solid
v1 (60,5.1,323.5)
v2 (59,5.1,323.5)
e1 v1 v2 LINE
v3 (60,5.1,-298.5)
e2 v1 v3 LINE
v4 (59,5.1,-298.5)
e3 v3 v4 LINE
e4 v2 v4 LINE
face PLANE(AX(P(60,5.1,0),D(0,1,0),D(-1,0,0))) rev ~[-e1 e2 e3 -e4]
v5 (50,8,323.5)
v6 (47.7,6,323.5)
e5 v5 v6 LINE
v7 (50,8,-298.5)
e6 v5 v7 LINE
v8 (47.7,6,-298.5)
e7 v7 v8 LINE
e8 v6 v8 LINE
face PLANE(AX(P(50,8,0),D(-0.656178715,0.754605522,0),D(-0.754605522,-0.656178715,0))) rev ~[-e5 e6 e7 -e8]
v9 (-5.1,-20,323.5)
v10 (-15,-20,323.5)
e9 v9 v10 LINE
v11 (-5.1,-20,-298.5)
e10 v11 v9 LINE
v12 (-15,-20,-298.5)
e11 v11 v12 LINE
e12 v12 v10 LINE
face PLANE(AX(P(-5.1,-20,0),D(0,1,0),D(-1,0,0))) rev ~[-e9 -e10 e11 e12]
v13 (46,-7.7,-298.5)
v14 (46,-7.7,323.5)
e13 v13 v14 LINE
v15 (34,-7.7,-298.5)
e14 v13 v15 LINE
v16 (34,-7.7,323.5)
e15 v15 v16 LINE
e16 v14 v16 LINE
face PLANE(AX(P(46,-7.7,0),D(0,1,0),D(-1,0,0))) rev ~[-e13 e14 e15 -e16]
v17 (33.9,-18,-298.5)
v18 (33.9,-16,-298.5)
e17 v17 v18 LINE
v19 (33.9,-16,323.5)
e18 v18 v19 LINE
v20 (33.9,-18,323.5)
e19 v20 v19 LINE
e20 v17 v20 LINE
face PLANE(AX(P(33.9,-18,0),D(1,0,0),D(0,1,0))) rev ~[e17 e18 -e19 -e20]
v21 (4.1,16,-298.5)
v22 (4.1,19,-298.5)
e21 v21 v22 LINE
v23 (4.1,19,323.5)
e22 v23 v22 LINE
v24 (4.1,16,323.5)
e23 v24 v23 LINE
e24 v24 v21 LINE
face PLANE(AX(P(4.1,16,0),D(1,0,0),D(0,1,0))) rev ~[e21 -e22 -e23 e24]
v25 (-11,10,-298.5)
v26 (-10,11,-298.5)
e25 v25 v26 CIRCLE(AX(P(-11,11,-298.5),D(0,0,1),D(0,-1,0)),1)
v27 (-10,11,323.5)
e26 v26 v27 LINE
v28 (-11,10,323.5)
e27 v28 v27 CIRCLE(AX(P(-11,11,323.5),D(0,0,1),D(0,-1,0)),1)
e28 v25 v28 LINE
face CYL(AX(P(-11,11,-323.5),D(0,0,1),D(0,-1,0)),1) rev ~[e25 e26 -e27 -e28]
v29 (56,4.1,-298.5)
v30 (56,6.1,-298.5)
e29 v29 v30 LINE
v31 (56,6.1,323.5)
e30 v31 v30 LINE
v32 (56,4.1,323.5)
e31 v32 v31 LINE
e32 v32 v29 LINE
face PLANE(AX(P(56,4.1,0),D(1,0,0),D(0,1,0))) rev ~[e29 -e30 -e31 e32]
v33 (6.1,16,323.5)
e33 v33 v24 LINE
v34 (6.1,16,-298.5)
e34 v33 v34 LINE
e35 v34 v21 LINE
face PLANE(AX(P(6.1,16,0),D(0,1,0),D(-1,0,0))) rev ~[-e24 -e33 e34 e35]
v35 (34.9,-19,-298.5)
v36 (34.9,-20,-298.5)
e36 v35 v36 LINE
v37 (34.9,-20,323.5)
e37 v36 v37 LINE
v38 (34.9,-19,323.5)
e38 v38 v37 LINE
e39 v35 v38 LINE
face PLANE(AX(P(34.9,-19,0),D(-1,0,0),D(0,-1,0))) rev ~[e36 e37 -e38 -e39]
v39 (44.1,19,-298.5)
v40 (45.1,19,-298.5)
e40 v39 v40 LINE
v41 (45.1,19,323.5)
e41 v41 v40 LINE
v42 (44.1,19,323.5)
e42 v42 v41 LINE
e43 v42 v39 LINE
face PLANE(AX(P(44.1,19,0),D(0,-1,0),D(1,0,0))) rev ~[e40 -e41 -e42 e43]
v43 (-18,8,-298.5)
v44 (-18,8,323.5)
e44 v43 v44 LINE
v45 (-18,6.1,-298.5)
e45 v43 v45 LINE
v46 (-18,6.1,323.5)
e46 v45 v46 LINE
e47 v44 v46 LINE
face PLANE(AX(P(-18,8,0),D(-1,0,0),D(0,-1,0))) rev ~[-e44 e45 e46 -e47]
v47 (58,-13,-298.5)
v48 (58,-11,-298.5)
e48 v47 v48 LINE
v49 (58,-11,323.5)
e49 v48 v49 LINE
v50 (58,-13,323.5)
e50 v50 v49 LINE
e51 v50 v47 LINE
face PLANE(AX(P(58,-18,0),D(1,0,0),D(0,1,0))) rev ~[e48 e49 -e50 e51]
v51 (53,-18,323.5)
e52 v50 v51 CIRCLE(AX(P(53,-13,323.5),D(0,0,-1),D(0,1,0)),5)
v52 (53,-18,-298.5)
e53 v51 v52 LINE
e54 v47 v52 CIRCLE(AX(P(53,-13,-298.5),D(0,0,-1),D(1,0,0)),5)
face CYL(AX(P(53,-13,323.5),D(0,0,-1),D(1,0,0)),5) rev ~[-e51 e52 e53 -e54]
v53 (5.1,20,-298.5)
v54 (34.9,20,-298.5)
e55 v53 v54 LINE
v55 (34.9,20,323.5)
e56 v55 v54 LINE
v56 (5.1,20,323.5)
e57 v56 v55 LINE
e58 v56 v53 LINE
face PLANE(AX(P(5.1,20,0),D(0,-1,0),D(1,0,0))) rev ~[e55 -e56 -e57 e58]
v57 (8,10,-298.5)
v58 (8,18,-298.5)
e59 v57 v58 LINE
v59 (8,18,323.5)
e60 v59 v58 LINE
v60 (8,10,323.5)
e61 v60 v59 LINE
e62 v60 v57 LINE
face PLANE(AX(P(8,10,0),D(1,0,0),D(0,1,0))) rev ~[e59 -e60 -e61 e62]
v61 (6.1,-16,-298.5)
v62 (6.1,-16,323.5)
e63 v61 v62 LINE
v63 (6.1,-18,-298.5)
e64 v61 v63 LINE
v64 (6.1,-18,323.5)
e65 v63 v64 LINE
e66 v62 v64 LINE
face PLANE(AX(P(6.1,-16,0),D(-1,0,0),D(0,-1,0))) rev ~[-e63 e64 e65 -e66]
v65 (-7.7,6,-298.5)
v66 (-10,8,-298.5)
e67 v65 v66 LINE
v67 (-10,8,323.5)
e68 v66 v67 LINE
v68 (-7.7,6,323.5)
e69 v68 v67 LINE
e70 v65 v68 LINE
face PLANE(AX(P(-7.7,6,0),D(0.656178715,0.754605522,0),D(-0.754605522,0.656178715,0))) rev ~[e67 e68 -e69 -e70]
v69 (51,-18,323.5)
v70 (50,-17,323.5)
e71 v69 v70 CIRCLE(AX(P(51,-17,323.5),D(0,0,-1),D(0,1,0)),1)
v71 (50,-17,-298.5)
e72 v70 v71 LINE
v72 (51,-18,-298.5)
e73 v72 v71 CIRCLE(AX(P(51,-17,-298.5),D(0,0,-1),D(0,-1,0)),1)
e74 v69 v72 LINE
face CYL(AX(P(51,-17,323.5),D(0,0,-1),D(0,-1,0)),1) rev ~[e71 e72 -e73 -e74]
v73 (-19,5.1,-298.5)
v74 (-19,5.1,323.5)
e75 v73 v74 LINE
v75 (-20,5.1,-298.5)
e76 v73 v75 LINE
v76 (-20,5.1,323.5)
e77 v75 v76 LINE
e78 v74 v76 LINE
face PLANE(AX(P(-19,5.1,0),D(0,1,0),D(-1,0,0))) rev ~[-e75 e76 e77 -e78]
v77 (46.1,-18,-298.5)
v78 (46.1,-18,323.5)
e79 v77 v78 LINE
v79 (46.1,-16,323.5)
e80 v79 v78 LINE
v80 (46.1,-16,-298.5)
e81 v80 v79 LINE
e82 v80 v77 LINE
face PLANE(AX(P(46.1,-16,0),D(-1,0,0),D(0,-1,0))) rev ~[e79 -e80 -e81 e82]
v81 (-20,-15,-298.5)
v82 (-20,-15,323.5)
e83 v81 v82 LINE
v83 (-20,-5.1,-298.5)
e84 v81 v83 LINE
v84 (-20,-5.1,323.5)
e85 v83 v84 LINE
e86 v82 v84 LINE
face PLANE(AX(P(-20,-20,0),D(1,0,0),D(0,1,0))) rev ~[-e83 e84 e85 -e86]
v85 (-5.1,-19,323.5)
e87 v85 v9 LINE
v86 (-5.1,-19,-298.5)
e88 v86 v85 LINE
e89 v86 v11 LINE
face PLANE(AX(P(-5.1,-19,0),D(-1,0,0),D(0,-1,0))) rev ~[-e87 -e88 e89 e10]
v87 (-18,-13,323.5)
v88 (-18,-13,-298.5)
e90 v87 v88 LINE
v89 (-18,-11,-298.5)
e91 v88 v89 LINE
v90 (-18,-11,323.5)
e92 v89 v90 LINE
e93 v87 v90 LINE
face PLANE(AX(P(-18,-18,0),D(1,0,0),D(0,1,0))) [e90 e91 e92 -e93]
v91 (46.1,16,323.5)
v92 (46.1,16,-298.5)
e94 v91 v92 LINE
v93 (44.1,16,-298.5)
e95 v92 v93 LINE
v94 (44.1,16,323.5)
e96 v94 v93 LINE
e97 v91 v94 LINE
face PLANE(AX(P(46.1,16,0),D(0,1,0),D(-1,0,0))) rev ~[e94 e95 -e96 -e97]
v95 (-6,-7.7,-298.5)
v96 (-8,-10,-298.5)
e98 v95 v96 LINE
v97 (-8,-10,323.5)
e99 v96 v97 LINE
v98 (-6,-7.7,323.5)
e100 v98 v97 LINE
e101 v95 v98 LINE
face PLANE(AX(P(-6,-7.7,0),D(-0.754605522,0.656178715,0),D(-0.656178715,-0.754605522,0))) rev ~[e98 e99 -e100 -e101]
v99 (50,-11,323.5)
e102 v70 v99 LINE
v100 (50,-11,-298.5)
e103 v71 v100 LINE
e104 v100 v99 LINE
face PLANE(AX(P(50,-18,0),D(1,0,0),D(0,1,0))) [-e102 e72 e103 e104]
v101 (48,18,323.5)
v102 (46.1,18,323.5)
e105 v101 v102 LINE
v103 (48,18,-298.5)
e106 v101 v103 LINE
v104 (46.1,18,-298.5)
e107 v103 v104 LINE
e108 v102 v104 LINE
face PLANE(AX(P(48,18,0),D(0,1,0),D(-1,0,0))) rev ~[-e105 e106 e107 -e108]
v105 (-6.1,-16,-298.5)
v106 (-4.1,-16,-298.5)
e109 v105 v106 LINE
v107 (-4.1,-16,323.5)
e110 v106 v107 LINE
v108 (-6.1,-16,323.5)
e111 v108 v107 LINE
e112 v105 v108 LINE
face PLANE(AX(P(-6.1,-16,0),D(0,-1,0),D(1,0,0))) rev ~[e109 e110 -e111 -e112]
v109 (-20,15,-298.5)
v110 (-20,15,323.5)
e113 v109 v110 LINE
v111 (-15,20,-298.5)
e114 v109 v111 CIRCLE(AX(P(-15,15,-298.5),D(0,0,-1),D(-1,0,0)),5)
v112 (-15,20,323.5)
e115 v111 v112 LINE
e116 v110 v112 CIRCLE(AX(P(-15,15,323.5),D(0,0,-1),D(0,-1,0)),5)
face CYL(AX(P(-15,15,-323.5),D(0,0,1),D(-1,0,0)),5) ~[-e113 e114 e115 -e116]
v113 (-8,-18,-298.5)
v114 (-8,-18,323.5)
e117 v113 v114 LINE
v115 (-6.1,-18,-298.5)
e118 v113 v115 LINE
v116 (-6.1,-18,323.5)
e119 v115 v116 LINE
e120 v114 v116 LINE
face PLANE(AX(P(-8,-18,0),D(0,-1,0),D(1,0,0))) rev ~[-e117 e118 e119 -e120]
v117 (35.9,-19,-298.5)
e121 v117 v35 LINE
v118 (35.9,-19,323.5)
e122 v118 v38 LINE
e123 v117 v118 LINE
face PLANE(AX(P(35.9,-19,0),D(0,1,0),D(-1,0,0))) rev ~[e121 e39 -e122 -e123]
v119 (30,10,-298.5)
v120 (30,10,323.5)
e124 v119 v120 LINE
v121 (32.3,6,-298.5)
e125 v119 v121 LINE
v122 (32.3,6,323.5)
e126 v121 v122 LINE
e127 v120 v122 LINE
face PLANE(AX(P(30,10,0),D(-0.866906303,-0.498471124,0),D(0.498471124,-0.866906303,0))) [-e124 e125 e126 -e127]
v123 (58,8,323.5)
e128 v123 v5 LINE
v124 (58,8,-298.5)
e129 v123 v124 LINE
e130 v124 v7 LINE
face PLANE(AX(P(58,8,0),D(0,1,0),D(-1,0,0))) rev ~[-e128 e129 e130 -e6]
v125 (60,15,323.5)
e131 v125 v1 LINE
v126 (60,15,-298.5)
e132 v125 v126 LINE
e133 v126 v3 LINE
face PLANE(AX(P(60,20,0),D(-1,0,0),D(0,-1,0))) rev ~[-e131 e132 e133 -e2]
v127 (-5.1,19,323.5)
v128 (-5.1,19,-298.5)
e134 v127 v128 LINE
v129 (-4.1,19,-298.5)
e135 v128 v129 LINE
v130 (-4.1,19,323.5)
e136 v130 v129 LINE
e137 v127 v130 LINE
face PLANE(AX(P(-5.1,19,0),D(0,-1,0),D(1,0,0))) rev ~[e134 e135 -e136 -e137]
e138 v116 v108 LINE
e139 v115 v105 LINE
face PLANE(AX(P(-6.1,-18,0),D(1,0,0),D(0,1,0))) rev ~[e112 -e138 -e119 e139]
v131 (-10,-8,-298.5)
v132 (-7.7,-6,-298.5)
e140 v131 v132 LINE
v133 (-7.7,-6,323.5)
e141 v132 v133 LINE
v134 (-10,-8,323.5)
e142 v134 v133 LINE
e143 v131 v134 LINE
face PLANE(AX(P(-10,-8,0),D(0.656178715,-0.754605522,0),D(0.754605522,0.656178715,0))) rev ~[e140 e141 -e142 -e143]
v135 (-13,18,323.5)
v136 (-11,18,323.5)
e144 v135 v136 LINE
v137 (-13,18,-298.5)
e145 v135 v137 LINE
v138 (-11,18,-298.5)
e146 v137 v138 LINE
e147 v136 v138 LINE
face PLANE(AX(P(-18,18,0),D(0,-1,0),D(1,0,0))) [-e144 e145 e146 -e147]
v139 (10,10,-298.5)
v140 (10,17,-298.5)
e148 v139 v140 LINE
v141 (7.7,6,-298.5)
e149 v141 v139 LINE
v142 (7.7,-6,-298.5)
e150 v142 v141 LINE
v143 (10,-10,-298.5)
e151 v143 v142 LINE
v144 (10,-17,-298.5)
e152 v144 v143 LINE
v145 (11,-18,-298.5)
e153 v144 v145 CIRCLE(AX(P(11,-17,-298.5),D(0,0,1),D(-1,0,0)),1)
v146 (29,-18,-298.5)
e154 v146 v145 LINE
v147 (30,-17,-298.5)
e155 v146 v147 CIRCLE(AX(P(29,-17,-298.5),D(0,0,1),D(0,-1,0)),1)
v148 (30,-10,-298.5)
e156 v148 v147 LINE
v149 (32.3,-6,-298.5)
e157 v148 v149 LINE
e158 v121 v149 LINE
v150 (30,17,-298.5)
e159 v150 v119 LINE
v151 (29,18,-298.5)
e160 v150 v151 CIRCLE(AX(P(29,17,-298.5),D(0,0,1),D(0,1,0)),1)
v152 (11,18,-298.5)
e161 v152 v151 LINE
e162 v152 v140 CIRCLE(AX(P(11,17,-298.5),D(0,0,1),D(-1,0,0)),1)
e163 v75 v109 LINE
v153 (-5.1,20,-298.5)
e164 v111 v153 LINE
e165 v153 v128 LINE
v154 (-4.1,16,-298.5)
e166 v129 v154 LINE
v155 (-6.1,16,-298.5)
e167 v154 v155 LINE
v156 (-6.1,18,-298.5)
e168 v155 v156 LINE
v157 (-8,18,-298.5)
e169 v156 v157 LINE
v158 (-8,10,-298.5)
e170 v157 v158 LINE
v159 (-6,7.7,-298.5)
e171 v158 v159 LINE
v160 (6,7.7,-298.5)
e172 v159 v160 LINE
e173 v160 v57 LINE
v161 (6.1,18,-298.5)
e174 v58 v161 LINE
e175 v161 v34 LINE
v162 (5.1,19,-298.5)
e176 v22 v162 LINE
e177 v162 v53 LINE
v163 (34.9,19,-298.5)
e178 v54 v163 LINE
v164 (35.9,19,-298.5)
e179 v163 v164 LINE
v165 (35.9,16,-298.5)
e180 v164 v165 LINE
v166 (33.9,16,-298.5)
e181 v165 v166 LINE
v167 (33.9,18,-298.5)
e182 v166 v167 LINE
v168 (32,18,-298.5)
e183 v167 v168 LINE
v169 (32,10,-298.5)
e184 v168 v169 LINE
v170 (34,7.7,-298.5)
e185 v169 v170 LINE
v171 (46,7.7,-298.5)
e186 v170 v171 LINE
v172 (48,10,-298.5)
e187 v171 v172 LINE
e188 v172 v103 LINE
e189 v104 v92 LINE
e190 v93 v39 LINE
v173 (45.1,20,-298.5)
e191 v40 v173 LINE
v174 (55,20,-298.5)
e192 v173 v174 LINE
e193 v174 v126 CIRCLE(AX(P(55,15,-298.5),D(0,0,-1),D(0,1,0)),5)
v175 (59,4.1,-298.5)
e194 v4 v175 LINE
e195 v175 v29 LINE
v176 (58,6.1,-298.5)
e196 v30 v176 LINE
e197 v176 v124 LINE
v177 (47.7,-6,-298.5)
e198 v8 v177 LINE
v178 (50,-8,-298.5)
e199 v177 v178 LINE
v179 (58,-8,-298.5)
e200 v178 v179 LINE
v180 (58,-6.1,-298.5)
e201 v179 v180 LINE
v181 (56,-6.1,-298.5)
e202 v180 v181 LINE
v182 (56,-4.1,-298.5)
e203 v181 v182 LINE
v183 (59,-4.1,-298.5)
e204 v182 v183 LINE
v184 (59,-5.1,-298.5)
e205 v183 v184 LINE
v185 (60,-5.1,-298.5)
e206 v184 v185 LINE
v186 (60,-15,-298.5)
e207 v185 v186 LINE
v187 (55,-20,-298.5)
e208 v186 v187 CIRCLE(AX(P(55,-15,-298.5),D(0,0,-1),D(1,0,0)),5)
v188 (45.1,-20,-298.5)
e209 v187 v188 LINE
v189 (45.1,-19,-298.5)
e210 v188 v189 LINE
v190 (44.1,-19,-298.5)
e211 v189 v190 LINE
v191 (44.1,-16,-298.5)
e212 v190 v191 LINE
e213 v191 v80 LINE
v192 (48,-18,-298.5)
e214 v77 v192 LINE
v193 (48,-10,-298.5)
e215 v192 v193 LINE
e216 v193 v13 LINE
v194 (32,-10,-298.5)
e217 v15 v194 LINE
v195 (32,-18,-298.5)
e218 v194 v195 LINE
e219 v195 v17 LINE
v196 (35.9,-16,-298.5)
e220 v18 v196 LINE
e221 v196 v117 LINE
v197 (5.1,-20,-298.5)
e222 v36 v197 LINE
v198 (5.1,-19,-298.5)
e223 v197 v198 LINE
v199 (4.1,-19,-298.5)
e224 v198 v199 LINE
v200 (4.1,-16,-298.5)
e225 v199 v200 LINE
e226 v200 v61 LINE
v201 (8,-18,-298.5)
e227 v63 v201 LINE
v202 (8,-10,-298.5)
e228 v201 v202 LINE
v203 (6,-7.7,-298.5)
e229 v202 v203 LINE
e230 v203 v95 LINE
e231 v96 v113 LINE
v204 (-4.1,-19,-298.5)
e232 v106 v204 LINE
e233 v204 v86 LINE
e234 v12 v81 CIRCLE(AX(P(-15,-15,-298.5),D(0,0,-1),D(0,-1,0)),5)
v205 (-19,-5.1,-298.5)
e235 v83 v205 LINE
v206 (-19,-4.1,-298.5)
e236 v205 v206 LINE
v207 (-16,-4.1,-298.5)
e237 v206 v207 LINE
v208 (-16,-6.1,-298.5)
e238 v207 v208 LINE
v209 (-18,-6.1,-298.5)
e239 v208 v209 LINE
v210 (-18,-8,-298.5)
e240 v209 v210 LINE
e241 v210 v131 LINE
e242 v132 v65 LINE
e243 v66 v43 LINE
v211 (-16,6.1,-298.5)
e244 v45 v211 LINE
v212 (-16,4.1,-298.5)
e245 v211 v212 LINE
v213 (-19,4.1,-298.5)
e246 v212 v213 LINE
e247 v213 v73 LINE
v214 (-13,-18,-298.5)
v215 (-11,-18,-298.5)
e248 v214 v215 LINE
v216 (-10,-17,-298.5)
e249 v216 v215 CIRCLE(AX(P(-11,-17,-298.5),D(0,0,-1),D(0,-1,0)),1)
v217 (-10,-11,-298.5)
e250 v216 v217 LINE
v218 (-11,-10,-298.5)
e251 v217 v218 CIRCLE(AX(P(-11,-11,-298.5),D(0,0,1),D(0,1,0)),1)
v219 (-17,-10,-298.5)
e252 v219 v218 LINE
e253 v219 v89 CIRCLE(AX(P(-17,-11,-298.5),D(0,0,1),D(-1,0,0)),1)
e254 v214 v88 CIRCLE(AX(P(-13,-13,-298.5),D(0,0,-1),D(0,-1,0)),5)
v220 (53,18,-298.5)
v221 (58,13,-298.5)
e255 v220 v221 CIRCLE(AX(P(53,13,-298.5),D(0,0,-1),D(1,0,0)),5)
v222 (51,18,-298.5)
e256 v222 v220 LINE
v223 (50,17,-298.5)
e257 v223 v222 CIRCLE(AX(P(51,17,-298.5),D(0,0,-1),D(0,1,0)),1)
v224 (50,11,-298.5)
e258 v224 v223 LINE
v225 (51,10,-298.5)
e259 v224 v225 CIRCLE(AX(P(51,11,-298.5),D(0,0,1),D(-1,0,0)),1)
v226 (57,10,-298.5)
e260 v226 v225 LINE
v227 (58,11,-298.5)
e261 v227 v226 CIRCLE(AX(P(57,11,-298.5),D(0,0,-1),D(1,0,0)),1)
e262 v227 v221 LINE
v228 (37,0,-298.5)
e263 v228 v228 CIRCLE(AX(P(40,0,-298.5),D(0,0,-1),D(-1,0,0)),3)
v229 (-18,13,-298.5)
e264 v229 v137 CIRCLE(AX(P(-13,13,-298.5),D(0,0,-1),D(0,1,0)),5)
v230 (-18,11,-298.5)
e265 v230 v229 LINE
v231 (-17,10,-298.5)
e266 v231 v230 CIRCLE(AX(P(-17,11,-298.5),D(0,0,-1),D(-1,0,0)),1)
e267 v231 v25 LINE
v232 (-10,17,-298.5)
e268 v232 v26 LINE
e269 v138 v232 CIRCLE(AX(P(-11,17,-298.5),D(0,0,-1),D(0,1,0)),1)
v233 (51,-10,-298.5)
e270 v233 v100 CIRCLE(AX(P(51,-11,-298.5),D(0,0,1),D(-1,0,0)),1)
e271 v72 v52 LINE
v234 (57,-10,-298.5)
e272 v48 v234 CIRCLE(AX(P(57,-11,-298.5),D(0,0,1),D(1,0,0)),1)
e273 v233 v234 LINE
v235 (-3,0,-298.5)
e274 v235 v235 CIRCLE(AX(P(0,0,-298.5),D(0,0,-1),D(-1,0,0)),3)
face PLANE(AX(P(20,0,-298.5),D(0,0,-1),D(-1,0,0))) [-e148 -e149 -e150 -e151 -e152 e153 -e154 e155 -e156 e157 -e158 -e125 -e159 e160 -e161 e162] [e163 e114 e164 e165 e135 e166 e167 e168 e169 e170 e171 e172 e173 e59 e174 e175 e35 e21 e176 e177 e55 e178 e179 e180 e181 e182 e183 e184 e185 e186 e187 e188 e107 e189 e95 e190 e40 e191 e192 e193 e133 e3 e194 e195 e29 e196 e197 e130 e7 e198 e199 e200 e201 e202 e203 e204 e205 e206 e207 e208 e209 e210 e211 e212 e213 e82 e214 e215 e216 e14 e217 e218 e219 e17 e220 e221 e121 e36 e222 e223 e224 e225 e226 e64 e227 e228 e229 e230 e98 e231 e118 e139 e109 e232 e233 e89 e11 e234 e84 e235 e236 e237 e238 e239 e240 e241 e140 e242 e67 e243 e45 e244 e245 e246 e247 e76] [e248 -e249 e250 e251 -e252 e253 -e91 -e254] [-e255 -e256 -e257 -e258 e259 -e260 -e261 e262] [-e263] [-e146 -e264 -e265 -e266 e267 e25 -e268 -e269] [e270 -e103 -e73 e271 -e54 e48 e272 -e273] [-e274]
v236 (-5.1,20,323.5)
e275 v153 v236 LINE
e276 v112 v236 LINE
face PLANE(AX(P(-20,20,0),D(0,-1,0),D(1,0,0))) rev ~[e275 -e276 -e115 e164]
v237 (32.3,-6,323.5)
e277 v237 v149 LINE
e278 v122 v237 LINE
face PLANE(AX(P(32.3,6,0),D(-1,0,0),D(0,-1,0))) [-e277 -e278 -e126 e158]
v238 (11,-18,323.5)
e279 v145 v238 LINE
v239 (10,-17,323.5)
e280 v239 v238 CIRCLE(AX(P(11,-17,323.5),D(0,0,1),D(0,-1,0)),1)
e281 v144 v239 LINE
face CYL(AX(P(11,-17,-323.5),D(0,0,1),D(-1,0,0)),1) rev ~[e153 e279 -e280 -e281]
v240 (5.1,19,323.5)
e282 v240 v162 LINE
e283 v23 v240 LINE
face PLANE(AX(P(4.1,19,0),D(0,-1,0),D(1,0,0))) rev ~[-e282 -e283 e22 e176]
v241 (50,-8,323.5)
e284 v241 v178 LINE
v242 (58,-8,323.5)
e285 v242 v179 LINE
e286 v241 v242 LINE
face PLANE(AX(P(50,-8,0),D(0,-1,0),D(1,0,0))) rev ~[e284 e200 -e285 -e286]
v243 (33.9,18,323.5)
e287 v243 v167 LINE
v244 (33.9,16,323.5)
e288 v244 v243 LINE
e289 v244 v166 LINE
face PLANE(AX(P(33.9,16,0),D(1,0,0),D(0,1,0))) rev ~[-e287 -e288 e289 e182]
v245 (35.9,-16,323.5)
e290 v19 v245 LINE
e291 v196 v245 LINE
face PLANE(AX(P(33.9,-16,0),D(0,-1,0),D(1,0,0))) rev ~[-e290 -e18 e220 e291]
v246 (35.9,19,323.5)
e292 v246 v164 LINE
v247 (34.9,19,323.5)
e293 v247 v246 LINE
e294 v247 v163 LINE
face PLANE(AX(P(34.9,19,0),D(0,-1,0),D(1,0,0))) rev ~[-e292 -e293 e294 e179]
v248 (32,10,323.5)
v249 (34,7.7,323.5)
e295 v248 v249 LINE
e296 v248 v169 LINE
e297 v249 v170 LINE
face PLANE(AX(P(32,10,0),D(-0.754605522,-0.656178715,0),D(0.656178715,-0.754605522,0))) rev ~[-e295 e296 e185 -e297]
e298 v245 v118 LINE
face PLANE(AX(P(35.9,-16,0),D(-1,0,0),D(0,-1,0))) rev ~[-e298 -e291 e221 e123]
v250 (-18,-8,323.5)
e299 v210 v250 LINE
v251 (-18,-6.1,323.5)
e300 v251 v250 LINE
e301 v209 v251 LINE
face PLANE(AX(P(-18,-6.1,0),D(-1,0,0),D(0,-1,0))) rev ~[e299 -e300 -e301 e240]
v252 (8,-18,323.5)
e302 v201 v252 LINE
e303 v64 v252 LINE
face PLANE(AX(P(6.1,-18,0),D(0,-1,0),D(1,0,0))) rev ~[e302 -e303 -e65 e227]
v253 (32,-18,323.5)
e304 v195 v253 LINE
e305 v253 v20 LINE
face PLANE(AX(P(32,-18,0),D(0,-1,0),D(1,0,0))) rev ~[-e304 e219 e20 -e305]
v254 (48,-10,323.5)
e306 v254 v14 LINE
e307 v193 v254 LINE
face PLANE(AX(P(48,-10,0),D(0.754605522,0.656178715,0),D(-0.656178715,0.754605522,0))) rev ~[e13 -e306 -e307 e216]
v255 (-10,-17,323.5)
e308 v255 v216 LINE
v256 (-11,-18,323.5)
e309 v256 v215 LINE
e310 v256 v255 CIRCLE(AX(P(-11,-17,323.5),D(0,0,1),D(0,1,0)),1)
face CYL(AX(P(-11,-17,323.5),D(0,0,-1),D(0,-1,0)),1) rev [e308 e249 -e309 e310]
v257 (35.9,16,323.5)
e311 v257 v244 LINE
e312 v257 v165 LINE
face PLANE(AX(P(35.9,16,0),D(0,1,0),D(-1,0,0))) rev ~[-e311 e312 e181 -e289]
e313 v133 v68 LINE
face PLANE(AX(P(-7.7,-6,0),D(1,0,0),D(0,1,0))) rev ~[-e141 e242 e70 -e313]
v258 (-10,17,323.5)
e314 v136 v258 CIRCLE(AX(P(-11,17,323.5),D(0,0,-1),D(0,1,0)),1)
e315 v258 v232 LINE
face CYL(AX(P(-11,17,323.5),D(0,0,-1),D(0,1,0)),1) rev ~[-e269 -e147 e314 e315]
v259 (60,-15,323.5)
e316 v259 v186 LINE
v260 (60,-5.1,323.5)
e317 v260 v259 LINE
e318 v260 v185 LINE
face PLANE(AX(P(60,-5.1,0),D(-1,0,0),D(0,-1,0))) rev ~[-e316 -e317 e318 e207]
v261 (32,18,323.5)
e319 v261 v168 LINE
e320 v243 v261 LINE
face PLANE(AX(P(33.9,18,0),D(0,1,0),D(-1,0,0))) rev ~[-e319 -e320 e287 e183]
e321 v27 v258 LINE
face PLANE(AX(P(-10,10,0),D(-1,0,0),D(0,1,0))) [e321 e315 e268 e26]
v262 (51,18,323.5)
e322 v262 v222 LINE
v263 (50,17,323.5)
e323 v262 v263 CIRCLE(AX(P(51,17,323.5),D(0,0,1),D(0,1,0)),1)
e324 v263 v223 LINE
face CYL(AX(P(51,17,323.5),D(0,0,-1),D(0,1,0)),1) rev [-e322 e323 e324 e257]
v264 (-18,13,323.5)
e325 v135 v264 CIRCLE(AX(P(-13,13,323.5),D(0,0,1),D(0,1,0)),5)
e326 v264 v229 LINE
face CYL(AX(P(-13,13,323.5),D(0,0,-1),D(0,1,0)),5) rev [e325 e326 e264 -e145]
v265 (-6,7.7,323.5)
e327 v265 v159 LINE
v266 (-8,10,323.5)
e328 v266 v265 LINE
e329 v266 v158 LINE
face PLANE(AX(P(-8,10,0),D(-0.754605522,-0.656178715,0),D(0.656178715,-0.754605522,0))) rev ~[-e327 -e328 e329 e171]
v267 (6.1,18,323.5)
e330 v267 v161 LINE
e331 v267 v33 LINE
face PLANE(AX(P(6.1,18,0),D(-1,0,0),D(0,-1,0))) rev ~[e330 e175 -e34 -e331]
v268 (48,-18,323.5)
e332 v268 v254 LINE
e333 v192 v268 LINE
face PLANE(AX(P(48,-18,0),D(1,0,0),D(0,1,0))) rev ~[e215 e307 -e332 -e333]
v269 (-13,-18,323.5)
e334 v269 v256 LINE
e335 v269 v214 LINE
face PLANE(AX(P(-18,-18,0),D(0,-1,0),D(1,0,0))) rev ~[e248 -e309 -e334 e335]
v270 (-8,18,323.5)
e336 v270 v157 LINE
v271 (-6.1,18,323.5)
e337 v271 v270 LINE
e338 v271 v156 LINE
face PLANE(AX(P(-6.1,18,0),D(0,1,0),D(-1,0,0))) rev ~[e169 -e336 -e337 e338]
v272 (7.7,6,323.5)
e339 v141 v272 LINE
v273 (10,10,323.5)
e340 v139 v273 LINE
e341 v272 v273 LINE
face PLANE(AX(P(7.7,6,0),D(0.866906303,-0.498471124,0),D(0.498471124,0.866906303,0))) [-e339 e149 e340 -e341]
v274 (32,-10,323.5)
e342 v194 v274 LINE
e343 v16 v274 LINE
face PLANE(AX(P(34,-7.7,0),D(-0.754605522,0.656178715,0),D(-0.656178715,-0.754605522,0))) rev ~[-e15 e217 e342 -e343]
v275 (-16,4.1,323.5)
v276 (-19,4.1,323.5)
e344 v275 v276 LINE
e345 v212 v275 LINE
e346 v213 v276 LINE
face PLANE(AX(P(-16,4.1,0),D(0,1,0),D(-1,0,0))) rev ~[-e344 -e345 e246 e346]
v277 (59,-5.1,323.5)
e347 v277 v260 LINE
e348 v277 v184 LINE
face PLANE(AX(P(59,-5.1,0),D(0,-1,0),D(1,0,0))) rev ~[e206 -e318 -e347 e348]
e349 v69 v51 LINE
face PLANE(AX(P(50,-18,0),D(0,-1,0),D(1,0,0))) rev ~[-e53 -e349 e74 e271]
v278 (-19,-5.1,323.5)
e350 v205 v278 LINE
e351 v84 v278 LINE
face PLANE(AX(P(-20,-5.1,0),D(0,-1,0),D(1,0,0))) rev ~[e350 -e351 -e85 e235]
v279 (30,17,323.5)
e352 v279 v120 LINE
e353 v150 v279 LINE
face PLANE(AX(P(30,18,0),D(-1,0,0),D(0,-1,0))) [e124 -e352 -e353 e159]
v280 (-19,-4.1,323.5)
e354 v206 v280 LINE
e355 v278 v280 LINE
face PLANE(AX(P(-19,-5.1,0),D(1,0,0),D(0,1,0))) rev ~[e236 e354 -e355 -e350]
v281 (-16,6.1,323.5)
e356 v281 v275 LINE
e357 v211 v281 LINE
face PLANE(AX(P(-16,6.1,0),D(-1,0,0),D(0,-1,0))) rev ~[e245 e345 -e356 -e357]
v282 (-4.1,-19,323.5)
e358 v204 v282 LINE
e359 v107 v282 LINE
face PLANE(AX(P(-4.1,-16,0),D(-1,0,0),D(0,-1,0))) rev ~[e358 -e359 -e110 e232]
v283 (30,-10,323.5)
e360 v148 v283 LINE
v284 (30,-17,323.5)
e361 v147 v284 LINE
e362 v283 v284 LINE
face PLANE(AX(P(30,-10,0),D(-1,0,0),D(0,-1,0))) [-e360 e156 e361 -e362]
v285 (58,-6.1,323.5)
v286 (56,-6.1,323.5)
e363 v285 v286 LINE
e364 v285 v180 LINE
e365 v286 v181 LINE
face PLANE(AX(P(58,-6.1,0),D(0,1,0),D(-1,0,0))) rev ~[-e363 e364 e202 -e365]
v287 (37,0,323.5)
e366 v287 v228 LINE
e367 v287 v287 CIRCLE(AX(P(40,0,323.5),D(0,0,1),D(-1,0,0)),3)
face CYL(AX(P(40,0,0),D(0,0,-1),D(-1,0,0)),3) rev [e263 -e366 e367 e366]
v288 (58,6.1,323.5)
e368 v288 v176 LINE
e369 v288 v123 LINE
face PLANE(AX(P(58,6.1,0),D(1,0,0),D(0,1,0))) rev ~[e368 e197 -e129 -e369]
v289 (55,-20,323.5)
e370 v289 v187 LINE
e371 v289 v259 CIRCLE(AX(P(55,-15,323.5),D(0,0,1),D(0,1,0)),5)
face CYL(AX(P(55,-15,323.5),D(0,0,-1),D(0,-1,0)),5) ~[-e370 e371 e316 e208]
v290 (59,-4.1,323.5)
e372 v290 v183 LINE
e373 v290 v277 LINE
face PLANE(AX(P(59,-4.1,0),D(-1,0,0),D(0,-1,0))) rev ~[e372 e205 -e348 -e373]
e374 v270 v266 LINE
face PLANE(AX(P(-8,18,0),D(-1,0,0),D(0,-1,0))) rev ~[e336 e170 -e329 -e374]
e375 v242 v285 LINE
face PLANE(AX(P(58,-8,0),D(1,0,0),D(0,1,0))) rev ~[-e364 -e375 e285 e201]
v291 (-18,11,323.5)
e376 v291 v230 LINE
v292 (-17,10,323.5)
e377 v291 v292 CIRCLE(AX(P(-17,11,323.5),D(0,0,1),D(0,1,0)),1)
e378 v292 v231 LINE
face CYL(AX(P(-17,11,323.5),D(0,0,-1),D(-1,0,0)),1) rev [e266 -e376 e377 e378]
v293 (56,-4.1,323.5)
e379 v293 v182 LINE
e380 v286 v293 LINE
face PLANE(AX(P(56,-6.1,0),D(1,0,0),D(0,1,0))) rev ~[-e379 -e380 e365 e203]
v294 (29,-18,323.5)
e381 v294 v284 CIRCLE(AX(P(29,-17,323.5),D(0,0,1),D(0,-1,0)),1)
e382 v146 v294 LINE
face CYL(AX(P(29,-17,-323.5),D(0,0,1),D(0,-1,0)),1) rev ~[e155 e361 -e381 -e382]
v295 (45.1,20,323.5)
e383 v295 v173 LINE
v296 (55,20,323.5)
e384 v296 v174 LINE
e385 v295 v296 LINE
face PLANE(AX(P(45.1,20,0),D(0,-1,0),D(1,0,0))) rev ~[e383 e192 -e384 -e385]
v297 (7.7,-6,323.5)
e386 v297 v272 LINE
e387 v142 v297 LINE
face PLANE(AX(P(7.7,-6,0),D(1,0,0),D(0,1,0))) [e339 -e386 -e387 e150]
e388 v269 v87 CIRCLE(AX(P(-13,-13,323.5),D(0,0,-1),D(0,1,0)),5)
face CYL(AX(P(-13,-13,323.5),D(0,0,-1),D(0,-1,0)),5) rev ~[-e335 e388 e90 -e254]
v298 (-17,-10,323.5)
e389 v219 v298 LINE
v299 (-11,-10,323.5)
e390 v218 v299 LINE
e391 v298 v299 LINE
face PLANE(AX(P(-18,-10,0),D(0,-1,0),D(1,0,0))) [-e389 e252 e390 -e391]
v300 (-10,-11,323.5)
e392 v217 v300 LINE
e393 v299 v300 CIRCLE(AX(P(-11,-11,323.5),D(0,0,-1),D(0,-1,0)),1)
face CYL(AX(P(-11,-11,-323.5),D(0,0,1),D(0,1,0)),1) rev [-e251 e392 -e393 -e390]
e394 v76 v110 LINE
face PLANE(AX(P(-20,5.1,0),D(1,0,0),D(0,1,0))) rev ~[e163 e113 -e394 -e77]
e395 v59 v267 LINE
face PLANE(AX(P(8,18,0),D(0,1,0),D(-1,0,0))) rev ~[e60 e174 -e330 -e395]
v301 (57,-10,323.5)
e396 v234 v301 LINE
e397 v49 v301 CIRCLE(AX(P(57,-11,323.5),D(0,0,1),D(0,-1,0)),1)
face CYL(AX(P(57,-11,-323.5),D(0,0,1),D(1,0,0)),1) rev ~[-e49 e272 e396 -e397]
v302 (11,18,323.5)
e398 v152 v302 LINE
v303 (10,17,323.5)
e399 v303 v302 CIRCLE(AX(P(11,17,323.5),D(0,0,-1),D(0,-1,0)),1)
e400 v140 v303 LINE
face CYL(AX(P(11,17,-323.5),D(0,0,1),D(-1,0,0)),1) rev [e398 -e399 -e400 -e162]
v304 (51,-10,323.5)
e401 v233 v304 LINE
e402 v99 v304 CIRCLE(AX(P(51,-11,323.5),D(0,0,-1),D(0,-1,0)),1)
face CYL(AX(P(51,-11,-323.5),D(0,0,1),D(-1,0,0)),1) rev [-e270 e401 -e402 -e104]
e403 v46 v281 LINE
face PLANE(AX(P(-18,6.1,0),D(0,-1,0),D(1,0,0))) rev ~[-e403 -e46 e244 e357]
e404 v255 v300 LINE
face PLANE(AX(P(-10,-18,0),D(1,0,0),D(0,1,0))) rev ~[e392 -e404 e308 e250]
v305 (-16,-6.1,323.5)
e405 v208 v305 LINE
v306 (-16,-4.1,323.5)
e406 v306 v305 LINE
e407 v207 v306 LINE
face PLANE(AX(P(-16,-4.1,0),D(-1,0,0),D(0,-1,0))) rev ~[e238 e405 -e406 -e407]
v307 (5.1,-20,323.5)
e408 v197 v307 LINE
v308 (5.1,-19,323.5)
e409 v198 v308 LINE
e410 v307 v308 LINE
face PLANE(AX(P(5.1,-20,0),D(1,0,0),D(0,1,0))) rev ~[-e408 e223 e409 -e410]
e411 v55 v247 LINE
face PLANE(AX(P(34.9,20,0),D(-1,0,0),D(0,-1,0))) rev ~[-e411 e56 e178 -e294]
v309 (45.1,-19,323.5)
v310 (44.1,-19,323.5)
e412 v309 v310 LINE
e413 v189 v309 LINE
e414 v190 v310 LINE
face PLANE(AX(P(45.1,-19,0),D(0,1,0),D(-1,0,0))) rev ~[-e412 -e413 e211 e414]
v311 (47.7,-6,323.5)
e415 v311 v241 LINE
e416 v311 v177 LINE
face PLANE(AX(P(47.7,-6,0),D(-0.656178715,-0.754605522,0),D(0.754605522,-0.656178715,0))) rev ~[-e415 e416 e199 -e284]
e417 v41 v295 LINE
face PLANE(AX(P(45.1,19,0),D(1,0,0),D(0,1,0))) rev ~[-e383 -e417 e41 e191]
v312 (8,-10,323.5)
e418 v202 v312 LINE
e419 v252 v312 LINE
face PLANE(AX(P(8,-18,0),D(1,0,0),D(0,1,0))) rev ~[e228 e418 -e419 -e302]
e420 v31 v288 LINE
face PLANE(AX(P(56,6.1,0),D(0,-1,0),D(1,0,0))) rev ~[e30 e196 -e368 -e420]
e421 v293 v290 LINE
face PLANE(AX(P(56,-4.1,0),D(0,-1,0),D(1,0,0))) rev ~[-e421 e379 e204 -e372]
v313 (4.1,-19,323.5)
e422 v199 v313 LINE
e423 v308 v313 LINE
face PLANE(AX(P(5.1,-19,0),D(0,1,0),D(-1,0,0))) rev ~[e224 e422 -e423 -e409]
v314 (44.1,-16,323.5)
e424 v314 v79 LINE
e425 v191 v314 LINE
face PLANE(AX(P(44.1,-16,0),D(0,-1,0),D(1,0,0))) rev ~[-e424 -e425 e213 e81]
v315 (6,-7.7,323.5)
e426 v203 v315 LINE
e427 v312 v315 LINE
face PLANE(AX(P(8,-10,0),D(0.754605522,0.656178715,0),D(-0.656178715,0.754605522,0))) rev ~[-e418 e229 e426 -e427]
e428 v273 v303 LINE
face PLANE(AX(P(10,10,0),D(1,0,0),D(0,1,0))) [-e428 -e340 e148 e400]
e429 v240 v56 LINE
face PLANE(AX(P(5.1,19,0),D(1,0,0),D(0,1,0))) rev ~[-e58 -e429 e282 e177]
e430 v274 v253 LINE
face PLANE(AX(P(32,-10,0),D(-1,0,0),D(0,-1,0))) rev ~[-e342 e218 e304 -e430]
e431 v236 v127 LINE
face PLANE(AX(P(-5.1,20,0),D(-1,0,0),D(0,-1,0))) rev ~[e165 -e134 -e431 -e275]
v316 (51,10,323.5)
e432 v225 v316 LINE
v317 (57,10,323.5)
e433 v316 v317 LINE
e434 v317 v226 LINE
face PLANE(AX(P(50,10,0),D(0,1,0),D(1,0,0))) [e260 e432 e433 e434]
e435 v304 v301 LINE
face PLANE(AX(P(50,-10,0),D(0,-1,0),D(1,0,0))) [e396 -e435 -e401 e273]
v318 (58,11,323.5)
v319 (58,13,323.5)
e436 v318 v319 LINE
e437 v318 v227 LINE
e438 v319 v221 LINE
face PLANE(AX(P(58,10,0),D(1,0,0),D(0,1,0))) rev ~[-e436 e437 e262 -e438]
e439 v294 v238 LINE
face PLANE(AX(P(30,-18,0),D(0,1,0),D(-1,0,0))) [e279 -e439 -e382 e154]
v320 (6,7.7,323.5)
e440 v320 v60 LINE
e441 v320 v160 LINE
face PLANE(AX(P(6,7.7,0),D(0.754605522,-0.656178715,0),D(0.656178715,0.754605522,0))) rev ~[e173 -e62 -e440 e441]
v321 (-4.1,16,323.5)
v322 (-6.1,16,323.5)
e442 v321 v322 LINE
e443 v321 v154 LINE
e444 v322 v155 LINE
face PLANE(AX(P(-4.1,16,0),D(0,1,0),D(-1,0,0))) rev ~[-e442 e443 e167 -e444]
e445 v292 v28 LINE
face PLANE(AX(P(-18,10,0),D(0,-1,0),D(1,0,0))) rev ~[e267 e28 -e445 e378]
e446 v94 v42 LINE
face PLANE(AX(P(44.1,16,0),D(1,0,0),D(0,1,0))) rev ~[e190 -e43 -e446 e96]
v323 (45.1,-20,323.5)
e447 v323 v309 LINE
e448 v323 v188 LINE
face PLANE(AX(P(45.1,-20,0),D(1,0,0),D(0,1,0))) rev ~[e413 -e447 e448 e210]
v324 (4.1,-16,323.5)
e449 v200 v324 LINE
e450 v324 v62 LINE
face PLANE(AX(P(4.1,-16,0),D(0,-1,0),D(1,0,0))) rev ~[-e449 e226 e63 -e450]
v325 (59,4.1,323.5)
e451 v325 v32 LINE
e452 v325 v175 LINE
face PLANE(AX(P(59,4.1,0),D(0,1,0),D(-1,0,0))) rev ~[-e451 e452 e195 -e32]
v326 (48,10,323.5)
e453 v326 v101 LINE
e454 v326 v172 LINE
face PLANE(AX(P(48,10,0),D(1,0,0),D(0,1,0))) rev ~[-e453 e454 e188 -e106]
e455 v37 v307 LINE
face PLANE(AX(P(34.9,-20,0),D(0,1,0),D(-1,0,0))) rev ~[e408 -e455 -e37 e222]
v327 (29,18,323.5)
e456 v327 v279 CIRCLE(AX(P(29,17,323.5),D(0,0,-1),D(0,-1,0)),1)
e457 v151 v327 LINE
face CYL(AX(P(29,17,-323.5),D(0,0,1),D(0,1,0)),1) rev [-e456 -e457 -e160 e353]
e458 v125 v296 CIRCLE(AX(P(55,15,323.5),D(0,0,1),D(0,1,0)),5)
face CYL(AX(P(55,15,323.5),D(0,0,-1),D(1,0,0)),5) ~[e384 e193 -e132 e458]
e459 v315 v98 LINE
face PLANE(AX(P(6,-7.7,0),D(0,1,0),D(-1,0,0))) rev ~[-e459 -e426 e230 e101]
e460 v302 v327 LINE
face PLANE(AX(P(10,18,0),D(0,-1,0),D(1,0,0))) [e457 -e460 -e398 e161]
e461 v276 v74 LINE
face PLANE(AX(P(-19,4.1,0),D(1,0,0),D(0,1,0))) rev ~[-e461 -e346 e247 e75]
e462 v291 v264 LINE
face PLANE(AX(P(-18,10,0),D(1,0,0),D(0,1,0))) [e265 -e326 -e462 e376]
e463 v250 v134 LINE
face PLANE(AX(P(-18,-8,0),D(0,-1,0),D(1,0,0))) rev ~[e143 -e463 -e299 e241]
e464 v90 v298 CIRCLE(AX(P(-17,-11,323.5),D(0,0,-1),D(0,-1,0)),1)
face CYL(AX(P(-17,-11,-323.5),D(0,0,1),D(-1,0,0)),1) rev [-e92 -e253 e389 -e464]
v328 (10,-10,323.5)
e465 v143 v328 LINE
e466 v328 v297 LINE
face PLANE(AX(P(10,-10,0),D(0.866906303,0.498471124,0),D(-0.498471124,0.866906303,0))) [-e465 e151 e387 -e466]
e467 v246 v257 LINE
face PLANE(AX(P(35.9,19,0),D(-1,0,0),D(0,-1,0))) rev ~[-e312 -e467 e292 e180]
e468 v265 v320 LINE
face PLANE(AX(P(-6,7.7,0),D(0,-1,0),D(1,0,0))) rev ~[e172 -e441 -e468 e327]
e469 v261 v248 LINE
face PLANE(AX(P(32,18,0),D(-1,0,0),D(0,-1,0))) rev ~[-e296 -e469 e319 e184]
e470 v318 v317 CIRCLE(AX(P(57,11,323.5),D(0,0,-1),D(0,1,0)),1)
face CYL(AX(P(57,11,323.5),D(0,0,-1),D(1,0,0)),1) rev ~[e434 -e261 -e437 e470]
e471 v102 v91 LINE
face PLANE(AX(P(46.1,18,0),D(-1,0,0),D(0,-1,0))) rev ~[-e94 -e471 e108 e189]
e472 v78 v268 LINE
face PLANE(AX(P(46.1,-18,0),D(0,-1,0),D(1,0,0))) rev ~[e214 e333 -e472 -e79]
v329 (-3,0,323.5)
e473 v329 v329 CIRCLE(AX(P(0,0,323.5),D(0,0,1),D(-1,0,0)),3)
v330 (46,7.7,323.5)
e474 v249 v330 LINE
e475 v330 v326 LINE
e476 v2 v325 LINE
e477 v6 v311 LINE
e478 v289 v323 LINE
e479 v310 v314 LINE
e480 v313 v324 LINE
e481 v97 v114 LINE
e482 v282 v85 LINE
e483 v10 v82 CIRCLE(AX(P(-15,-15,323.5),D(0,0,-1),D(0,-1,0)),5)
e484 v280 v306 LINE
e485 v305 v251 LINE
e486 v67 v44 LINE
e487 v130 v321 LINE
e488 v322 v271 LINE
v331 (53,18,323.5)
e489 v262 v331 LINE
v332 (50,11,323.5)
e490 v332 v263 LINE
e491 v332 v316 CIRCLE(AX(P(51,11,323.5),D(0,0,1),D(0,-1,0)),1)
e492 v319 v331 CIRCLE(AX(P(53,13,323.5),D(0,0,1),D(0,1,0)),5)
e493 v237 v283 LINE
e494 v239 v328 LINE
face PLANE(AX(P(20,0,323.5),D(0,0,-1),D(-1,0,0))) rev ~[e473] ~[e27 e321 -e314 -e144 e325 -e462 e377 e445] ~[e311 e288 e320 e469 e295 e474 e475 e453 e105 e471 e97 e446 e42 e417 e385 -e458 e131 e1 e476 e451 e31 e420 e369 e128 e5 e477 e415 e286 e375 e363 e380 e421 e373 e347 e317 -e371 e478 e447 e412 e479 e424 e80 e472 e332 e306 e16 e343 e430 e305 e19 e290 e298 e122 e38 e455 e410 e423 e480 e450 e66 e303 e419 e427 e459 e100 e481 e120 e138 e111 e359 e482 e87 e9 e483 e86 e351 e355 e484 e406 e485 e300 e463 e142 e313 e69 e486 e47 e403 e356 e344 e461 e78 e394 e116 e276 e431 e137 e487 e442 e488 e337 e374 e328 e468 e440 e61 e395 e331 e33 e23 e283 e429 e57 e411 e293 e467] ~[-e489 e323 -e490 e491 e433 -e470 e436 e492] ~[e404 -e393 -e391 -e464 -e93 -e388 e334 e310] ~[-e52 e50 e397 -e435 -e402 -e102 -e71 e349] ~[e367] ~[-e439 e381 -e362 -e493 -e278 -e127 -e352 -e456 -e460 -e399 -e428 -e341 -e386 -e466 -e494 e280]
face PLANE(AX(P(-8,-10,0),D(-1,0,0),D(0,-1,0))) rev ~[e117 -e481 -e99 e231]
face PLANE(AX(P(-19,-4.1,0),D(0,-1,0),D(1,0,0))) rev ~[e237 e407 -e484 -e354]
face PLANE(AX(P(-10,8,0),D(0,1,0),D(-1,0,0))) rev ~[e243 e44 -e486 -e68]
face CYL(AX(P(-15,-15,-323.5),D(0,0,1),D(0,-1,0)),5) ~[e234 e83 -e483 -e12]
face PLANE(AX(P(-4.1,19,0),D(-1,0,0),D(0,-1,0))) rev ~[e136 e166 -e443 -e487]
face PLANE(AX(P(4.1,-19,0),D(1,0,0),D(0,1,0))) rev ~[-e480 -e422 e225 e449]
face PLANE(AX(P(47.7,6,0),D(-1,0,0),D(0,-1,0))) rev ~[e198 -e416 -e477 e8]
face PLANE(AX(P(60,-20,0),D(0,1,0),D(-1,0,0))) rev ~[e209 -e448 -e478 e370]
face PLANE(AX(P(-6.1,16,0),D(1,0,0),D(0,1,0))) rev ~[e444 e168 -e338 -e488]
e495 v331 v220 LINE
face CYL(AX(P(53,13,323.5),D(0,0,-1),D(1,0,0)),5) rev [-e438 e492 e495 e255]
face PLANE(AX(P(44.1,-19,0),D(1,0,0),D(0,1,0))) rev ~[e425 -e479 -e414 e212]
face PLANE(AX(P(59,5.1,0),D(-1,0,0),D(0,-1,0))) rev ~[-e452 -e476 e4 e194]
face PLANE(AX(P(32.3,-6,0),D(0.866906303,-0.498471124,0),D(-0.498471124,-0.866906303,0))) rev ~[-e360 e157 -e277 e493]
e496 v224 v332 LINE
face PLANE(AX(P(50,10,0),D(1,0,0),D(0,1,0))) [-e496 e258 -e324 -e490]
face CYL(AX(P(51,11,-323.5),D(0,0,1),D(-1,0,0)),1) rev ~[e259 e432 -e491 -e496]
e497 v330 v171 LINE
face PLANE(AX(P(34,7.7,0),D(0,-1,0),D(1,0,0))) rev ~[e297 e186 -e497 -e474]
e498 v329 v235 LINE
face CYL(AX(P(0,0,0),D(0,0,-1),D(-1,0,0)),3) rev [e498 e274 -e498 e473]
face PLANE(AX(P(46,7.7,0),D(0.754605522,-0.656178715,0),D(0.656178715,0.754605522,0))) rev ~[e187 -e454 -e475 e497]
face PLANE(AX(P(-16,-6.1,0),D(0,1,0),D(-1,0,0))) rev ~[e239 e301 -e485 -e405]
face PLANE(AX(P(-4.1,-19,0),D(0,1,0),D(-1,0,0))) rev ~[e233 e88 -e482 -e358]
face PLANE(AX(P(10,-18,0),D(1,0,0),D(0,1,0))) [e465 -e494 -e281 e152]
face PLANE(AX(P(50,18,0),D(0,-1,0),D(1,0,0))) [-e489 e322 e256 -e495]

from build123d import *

# Parameters (mm, degrees)
SKETCH_1_R          = 3
SKETCH_1_W          = 8
SKETCH_1_H          = 8
EXTRUDE_1_DEPTH     = 323.5
FILLET_1_R          = 5
FILLET_2_R          = 1
CUT_EXTRUDE_1_DEPTH = 25


with BuildPart() as part:
    # 草图1 → 拉伸1 (new, symmetric)
    with BuildSketch(Plane.XY):
        Polygon((-5.1, 20), (-5.1, 19), (-4.1, 19), (-4.1, 16), (-6.1, 16), (-6.1, 18), (-8, 18), (-8, 10), (-6, 7.7), (6, 7.7), (8, 10), (8, 18), (6.1, 18), (6.1, 16), (4.1, 16), (4.1, 19), (5.1, 19), (5.1, 20), (34.9, 20), (34.9, 19), (35.9, 19), (35.9, 16), (33.9, 16), (33.9, 18), (32, 18), (32, 10), (34, 7.7), (46, 7.7), (48, 10), (48, 18), (46.1, 18), (46.1, 16), (44.1, 16), (44.1, 19), (45.1, 19), (45.1, 20), (60, 20), (60, 5.1), (59, 5.1), (59, 4.1), (56, 4.1), (56, 6.1), (58, 6.1), (58, 8), (50, 8), (47.7, 6), (47.7, -6), (50, -8), (58, -8), (58, -6.1), (56, -6.1), (56, -4.1), (59, -4.1), (59, -5.1), (60, -5.1), (60, -20), (45.1, -20), (45.1, -19), (44.1, -19), (44.1, -16), (46.1, -16), (46.1, -18), (48, -18), (48, -10), (46, -7.7), (34, -7.7), (32, -10), (32, -18), (33.9, -18), (33.9, -16), (35.9, -16), (35.9, -19), (34.9, -19), (34.9, -20), (5.1, -20), (5.1, -19), (4.1, -19), (4.1, -16), (6.1, -16), (6.1, -18), (8, -18), (8, -10), (6, -7.7), (-6, -7.7), (-8, -10), (-8, -18), (-6.1, -18), (-6.1, -16), (-4.1, -16), (-4.1, -19), (-5.1, -19), (-5.1, -20), (-20, -20), (-20, -5.1), (-19, -5.1), (-19, -4.1), (-16, -4.1), (-16, -6.1), (-18, -6.1), (-18, -8), (-10, -8), (-7.7, -6), (-7.7, 6), (-10, 8), (-18, 8), (-18, 6.1), (-16, 6.1), (-16, 4.1), (-19, 4.1), (-19, 5.1), (-20, 5.1), (-20, 20), align=None)
        with Locations(Location((0, 0, 0), (0, 0, 180))):
            Circle(SKETCH_1_R, mode=Mode.SUBTRACT)
        with Locations(Location((40, 0, 0), (0, 0, 180))):
            Circle(SKETCH_1_R, mode=Mode.SUBTRACT)
        Polygon((7.7, 6), (10, 10), (10, 18), (30, 18), (30, 10), (32.3, 6), (32.3, -6), (30, -10), (30, -18), (10, -18), (10, -10), (7.7, -6), align=None, mode=Mode.SUBTRACT)
        with Locations((-14, 14)):
            Rectangle(SKETCH_1_W, SKETCH_1_H, mode=Mode.SUBTRACT)
        with Locations((-14, -14)):
            Rectangle(SKETCH_1_W, SKETCH_1_H, mode=Mode.SUBTRACT)
        with Locations((54, -14)):
            Rectangle(SKETCH_1_W, SKETCH_1_H, mode=Mode.SUBTRACT)
        with Locations((54, 14)):
            Rectangle(SKETCH_1_W, SKETCH_1_H, mode=Mode.SUBTRACT)
    extrude(amount=EXTRUDE_1_DEPTH, both=True)

    # 圆角1
    fillet_1_edges = [part.edges().sort_by_distance(p)[0] for p in [
        (-20, 20, 0),
        (60, 20, 0),
        (60, -20, 0),
        (-20, -20, 0),
        (-18, 18, 0),
        (-18, -18, 0),
        (58, -18, 0),
        (58, 18, 0),
    ]]
    fillet(fillet_1_edges, radius=FILLET_1_R)

    # 圆角2
    fillet_2_edges = [part.edges().sort_by_distance(p)[0] for p in [
        (10, -18, 0),
        (30, -18, 0),
        (30, 18, 0),
        (10, 18, 0),
        (-18, 10, 0),
        (-10, 10, 0),
        (-10, 18, 0),
        (-10, -18, 0),
        (-10, -10, 0),
        (-18, -10, 0),
        (58, -10, 0),
        (50, -10, 0),
        (50, -18, 0),
        (50, 18, 0),
        (50, 10, 0),
        (58, 10, 0),
    ]]
    fillet(fillet_2_edges, radius=FILLET_2_R)

    # 草图4 → 切除-拉伸1 (cut)
    with BuildSketch(Plane(origin=(0, 0, -323.5), x_dir=(-1, 0, 0), z_dir=(0, 0, -1))):
        with BuildLine():
            Line((-60, -5.1), (-60, -15))
            ThreePointArc((-60, -15), (-58.535533906, -18.535533906), (-55, -20))
            Line((-55, -20), (-45.1, -20))
            Line((-45.1, -20), (-45.1, -19))
            Line((-45.1, -19), (-44.1, -19))
            Line((-44.1, -19), (-44.1, -16))
            Line((-44.1, -16), (-46.1, -16))
            Line((-46.1, -16), (-46.1, -18))
            Line((-46.1, -18), (-48, -18))
            Line((-48, -18), (-48, -10))
            Line((-48, -10), (-46, -7.7))
            Line((-46, -7.7), (-34, -7.7))
            Line((-34, -7.7), (-32, -10))
            Line((-32, -10), (-32, -18))
            Line((-32, -18), (-33.9, -18))
            Line((-33.9, -18), (-33.9, -16))
            Line((-33.9, -16), (-35.9, -16))
            Line((-35.9, -16), (-35.9, -19))
            Line((-35.9, -19), (-34.9, -19))
            Line((-34.9, -19), (-34.9, -20))
            Line((-34.9, -20), (-5.1, -20))
            Line((-5.1, -20), (-5.1, -19))
            Line((-5.1, -19), (-4.1, -19))
            Line((-4.1, -19), (-4.1, -16))
            Line((-4.1, -16), (-6.1, -16))
            Line((-6.1, -16), (-6.1, -18))
            Line((-6.1, -18), (-8, -18))
            Line((-8, -18), (-8, -10))
            Line((-8, -10), (-6, -7.7))
            Line((-6, -7.7), (6, -7.7))
            Line((6, -7.7), (8, -10))
            Line((8, -10), (8, -18))
            Line((8, -18), (6.1, -18))
            Line((6.1, -18), (6.1, -16))
            Line((6.1, -16), (4.1, -16))
            Line((4.1, -16), (4.1, -19))
            Line((4.1, -19), (5.1, -19))
            Line((5.1, -19), (5.1, -20))
            Line((5.1, -20), (15, -20))
            ThreePointArc((15, -20), (18.535533906, -18.535533906), (20, -15))
            Line((20, -15), (20, -5.1))
            Line((20, -5.1), (19, -5.1))
            Line((19, -5.1), (19, -4.1))
            Line((19, -4.1), (16, -4.1))
            Line((16, -4.1), (16, -6.1))
            Line((16, -6.1), (18, -6.1))
            Line((18, -6.1), (18, -8))
            Line((18, -8), (10, -8))
            Line((10, -8), (7.7, -6))
            Line((7.7, -6), (7.7, 6))
            Line((7.7, 6), (10, 8))
            Line((10, 8), (18, 8))
            Line((18, 8), (18, 6.1))
            Line((18, 6.1), (16, 6.1))
            Line((16, 6.1), (16, 4.1))
            Line((16, 4.1), (19, 4.1))
            Line((19, 4.1), (19, 5.1))
            Line((19, 5.1), (20, 5.1))
            Line((20, 5.1), (20, 15))
            ThreePointArc((20, 15), (18.535533906, 18.535533906), (15, 20))
            Line((15, 20), (5.1, 20))
            Line((5.1, 20), (5.1, 19))
            Line((5.1, 19), (4.1, 19))
            Line((4.1, 19), (4.1, 16))
            Line((4.1, 16), (6.1, 16))
            Line((6.1, 16), (6.1, 18))
            Line((6.1, 18), (8, 18))
            Line((8, 18), (8, 10))
            Line((8, 10), (6, 7.7))
            Line((6, 7.7), (-6, 7.7))
            Line((-6, 7.7), (-8, 10))
            Line((-8, 10), (-8, 18))
            Line((-8, 18), (-6.1, 18))
            Line((-6.1, 18), (-6.1, 16))
            Line((-6.1, 16), (-4.1, 16))
            Line((-4.1, 16), (-4.1, 19))
            Line((-4.1, 19), (-5.1, 19))
            Line((-5.1, 19), (-5.1, 20))
            Line((-5.1, 20), (-34.9, 20))
            Line((-34.9, 20), (-34.9, 19))
            Line((-34.9, 19), (-35.9, 19))
            Line((-35.9, 19), (-35.9, 16))
            Line((-35.9, 16), (-33.9, 16))
            Line((-33.9, 16), (-33.9, 18))
            Line((-33.9, 18), (-32, 18))
            Line((-32, 18), (-32, 10))
            Line((-32, 10), (-34, 7.7))
            Line((-34, 7.7), (-46, 7.7))
            Line((-46, 7.7), (-48, 10))
            Line((-48, 10), (-48, 18))
            Line((-48, 18), (-46.1, 18))
            Line((-46.1, 18), (-46.1, 16))
            Line((-46.1, 16), (-44.1, 16))
            Line((-44.1, 16), (-44.1, 19))
            Line((-44.1, 19), (-45.1, 19))
            Line((-45.1, 19), (-45.1, 20))
            Line((-45.1, 20), (-55, 20))
            ThreePointArc((-55, 20), (-58.535533906, 18.535533906), (-60, 15))
            Line((-60, 15), (-60, 5.1))
            Line((-60, 5.1), (-59, 5.1))
            Line((-59, 5.1), (-59, 4.1))
            Line((-59, 4.1), (-56, 4.1))
            Line((-56, 4.1), (-56, 6.1))
            Line((-56, 6.1), (-58, 6.1))
            Line((-58, 6.1), (-58, 8))
            Line((-58, 8), (-50, 8))
            Line((-50, 8), (-47.7, 6))
            Line((-47.7, 6), (-47.7, -6))
            Line((-47.7, -6), (-50, -8))
            Line((-50, -8), (-58, -8))
            Line((-58, -8), (-58, -6.1))
            Line((-58, -6.1), (-56, -6.1))
            Line((-56, -6.1), (-56, -4.1))
            Line((-56, -4.1), (-59, -4.1))
            Line((-59, -4.1), (-59, -5.1))
            Line((-59, -5.1), (-60, -5.1))
        make_face()
    extrude(amount=-CUT_EXTRUDE_1_DEPTH, mode=Mode.SUBTRACT)


solid = part.part
